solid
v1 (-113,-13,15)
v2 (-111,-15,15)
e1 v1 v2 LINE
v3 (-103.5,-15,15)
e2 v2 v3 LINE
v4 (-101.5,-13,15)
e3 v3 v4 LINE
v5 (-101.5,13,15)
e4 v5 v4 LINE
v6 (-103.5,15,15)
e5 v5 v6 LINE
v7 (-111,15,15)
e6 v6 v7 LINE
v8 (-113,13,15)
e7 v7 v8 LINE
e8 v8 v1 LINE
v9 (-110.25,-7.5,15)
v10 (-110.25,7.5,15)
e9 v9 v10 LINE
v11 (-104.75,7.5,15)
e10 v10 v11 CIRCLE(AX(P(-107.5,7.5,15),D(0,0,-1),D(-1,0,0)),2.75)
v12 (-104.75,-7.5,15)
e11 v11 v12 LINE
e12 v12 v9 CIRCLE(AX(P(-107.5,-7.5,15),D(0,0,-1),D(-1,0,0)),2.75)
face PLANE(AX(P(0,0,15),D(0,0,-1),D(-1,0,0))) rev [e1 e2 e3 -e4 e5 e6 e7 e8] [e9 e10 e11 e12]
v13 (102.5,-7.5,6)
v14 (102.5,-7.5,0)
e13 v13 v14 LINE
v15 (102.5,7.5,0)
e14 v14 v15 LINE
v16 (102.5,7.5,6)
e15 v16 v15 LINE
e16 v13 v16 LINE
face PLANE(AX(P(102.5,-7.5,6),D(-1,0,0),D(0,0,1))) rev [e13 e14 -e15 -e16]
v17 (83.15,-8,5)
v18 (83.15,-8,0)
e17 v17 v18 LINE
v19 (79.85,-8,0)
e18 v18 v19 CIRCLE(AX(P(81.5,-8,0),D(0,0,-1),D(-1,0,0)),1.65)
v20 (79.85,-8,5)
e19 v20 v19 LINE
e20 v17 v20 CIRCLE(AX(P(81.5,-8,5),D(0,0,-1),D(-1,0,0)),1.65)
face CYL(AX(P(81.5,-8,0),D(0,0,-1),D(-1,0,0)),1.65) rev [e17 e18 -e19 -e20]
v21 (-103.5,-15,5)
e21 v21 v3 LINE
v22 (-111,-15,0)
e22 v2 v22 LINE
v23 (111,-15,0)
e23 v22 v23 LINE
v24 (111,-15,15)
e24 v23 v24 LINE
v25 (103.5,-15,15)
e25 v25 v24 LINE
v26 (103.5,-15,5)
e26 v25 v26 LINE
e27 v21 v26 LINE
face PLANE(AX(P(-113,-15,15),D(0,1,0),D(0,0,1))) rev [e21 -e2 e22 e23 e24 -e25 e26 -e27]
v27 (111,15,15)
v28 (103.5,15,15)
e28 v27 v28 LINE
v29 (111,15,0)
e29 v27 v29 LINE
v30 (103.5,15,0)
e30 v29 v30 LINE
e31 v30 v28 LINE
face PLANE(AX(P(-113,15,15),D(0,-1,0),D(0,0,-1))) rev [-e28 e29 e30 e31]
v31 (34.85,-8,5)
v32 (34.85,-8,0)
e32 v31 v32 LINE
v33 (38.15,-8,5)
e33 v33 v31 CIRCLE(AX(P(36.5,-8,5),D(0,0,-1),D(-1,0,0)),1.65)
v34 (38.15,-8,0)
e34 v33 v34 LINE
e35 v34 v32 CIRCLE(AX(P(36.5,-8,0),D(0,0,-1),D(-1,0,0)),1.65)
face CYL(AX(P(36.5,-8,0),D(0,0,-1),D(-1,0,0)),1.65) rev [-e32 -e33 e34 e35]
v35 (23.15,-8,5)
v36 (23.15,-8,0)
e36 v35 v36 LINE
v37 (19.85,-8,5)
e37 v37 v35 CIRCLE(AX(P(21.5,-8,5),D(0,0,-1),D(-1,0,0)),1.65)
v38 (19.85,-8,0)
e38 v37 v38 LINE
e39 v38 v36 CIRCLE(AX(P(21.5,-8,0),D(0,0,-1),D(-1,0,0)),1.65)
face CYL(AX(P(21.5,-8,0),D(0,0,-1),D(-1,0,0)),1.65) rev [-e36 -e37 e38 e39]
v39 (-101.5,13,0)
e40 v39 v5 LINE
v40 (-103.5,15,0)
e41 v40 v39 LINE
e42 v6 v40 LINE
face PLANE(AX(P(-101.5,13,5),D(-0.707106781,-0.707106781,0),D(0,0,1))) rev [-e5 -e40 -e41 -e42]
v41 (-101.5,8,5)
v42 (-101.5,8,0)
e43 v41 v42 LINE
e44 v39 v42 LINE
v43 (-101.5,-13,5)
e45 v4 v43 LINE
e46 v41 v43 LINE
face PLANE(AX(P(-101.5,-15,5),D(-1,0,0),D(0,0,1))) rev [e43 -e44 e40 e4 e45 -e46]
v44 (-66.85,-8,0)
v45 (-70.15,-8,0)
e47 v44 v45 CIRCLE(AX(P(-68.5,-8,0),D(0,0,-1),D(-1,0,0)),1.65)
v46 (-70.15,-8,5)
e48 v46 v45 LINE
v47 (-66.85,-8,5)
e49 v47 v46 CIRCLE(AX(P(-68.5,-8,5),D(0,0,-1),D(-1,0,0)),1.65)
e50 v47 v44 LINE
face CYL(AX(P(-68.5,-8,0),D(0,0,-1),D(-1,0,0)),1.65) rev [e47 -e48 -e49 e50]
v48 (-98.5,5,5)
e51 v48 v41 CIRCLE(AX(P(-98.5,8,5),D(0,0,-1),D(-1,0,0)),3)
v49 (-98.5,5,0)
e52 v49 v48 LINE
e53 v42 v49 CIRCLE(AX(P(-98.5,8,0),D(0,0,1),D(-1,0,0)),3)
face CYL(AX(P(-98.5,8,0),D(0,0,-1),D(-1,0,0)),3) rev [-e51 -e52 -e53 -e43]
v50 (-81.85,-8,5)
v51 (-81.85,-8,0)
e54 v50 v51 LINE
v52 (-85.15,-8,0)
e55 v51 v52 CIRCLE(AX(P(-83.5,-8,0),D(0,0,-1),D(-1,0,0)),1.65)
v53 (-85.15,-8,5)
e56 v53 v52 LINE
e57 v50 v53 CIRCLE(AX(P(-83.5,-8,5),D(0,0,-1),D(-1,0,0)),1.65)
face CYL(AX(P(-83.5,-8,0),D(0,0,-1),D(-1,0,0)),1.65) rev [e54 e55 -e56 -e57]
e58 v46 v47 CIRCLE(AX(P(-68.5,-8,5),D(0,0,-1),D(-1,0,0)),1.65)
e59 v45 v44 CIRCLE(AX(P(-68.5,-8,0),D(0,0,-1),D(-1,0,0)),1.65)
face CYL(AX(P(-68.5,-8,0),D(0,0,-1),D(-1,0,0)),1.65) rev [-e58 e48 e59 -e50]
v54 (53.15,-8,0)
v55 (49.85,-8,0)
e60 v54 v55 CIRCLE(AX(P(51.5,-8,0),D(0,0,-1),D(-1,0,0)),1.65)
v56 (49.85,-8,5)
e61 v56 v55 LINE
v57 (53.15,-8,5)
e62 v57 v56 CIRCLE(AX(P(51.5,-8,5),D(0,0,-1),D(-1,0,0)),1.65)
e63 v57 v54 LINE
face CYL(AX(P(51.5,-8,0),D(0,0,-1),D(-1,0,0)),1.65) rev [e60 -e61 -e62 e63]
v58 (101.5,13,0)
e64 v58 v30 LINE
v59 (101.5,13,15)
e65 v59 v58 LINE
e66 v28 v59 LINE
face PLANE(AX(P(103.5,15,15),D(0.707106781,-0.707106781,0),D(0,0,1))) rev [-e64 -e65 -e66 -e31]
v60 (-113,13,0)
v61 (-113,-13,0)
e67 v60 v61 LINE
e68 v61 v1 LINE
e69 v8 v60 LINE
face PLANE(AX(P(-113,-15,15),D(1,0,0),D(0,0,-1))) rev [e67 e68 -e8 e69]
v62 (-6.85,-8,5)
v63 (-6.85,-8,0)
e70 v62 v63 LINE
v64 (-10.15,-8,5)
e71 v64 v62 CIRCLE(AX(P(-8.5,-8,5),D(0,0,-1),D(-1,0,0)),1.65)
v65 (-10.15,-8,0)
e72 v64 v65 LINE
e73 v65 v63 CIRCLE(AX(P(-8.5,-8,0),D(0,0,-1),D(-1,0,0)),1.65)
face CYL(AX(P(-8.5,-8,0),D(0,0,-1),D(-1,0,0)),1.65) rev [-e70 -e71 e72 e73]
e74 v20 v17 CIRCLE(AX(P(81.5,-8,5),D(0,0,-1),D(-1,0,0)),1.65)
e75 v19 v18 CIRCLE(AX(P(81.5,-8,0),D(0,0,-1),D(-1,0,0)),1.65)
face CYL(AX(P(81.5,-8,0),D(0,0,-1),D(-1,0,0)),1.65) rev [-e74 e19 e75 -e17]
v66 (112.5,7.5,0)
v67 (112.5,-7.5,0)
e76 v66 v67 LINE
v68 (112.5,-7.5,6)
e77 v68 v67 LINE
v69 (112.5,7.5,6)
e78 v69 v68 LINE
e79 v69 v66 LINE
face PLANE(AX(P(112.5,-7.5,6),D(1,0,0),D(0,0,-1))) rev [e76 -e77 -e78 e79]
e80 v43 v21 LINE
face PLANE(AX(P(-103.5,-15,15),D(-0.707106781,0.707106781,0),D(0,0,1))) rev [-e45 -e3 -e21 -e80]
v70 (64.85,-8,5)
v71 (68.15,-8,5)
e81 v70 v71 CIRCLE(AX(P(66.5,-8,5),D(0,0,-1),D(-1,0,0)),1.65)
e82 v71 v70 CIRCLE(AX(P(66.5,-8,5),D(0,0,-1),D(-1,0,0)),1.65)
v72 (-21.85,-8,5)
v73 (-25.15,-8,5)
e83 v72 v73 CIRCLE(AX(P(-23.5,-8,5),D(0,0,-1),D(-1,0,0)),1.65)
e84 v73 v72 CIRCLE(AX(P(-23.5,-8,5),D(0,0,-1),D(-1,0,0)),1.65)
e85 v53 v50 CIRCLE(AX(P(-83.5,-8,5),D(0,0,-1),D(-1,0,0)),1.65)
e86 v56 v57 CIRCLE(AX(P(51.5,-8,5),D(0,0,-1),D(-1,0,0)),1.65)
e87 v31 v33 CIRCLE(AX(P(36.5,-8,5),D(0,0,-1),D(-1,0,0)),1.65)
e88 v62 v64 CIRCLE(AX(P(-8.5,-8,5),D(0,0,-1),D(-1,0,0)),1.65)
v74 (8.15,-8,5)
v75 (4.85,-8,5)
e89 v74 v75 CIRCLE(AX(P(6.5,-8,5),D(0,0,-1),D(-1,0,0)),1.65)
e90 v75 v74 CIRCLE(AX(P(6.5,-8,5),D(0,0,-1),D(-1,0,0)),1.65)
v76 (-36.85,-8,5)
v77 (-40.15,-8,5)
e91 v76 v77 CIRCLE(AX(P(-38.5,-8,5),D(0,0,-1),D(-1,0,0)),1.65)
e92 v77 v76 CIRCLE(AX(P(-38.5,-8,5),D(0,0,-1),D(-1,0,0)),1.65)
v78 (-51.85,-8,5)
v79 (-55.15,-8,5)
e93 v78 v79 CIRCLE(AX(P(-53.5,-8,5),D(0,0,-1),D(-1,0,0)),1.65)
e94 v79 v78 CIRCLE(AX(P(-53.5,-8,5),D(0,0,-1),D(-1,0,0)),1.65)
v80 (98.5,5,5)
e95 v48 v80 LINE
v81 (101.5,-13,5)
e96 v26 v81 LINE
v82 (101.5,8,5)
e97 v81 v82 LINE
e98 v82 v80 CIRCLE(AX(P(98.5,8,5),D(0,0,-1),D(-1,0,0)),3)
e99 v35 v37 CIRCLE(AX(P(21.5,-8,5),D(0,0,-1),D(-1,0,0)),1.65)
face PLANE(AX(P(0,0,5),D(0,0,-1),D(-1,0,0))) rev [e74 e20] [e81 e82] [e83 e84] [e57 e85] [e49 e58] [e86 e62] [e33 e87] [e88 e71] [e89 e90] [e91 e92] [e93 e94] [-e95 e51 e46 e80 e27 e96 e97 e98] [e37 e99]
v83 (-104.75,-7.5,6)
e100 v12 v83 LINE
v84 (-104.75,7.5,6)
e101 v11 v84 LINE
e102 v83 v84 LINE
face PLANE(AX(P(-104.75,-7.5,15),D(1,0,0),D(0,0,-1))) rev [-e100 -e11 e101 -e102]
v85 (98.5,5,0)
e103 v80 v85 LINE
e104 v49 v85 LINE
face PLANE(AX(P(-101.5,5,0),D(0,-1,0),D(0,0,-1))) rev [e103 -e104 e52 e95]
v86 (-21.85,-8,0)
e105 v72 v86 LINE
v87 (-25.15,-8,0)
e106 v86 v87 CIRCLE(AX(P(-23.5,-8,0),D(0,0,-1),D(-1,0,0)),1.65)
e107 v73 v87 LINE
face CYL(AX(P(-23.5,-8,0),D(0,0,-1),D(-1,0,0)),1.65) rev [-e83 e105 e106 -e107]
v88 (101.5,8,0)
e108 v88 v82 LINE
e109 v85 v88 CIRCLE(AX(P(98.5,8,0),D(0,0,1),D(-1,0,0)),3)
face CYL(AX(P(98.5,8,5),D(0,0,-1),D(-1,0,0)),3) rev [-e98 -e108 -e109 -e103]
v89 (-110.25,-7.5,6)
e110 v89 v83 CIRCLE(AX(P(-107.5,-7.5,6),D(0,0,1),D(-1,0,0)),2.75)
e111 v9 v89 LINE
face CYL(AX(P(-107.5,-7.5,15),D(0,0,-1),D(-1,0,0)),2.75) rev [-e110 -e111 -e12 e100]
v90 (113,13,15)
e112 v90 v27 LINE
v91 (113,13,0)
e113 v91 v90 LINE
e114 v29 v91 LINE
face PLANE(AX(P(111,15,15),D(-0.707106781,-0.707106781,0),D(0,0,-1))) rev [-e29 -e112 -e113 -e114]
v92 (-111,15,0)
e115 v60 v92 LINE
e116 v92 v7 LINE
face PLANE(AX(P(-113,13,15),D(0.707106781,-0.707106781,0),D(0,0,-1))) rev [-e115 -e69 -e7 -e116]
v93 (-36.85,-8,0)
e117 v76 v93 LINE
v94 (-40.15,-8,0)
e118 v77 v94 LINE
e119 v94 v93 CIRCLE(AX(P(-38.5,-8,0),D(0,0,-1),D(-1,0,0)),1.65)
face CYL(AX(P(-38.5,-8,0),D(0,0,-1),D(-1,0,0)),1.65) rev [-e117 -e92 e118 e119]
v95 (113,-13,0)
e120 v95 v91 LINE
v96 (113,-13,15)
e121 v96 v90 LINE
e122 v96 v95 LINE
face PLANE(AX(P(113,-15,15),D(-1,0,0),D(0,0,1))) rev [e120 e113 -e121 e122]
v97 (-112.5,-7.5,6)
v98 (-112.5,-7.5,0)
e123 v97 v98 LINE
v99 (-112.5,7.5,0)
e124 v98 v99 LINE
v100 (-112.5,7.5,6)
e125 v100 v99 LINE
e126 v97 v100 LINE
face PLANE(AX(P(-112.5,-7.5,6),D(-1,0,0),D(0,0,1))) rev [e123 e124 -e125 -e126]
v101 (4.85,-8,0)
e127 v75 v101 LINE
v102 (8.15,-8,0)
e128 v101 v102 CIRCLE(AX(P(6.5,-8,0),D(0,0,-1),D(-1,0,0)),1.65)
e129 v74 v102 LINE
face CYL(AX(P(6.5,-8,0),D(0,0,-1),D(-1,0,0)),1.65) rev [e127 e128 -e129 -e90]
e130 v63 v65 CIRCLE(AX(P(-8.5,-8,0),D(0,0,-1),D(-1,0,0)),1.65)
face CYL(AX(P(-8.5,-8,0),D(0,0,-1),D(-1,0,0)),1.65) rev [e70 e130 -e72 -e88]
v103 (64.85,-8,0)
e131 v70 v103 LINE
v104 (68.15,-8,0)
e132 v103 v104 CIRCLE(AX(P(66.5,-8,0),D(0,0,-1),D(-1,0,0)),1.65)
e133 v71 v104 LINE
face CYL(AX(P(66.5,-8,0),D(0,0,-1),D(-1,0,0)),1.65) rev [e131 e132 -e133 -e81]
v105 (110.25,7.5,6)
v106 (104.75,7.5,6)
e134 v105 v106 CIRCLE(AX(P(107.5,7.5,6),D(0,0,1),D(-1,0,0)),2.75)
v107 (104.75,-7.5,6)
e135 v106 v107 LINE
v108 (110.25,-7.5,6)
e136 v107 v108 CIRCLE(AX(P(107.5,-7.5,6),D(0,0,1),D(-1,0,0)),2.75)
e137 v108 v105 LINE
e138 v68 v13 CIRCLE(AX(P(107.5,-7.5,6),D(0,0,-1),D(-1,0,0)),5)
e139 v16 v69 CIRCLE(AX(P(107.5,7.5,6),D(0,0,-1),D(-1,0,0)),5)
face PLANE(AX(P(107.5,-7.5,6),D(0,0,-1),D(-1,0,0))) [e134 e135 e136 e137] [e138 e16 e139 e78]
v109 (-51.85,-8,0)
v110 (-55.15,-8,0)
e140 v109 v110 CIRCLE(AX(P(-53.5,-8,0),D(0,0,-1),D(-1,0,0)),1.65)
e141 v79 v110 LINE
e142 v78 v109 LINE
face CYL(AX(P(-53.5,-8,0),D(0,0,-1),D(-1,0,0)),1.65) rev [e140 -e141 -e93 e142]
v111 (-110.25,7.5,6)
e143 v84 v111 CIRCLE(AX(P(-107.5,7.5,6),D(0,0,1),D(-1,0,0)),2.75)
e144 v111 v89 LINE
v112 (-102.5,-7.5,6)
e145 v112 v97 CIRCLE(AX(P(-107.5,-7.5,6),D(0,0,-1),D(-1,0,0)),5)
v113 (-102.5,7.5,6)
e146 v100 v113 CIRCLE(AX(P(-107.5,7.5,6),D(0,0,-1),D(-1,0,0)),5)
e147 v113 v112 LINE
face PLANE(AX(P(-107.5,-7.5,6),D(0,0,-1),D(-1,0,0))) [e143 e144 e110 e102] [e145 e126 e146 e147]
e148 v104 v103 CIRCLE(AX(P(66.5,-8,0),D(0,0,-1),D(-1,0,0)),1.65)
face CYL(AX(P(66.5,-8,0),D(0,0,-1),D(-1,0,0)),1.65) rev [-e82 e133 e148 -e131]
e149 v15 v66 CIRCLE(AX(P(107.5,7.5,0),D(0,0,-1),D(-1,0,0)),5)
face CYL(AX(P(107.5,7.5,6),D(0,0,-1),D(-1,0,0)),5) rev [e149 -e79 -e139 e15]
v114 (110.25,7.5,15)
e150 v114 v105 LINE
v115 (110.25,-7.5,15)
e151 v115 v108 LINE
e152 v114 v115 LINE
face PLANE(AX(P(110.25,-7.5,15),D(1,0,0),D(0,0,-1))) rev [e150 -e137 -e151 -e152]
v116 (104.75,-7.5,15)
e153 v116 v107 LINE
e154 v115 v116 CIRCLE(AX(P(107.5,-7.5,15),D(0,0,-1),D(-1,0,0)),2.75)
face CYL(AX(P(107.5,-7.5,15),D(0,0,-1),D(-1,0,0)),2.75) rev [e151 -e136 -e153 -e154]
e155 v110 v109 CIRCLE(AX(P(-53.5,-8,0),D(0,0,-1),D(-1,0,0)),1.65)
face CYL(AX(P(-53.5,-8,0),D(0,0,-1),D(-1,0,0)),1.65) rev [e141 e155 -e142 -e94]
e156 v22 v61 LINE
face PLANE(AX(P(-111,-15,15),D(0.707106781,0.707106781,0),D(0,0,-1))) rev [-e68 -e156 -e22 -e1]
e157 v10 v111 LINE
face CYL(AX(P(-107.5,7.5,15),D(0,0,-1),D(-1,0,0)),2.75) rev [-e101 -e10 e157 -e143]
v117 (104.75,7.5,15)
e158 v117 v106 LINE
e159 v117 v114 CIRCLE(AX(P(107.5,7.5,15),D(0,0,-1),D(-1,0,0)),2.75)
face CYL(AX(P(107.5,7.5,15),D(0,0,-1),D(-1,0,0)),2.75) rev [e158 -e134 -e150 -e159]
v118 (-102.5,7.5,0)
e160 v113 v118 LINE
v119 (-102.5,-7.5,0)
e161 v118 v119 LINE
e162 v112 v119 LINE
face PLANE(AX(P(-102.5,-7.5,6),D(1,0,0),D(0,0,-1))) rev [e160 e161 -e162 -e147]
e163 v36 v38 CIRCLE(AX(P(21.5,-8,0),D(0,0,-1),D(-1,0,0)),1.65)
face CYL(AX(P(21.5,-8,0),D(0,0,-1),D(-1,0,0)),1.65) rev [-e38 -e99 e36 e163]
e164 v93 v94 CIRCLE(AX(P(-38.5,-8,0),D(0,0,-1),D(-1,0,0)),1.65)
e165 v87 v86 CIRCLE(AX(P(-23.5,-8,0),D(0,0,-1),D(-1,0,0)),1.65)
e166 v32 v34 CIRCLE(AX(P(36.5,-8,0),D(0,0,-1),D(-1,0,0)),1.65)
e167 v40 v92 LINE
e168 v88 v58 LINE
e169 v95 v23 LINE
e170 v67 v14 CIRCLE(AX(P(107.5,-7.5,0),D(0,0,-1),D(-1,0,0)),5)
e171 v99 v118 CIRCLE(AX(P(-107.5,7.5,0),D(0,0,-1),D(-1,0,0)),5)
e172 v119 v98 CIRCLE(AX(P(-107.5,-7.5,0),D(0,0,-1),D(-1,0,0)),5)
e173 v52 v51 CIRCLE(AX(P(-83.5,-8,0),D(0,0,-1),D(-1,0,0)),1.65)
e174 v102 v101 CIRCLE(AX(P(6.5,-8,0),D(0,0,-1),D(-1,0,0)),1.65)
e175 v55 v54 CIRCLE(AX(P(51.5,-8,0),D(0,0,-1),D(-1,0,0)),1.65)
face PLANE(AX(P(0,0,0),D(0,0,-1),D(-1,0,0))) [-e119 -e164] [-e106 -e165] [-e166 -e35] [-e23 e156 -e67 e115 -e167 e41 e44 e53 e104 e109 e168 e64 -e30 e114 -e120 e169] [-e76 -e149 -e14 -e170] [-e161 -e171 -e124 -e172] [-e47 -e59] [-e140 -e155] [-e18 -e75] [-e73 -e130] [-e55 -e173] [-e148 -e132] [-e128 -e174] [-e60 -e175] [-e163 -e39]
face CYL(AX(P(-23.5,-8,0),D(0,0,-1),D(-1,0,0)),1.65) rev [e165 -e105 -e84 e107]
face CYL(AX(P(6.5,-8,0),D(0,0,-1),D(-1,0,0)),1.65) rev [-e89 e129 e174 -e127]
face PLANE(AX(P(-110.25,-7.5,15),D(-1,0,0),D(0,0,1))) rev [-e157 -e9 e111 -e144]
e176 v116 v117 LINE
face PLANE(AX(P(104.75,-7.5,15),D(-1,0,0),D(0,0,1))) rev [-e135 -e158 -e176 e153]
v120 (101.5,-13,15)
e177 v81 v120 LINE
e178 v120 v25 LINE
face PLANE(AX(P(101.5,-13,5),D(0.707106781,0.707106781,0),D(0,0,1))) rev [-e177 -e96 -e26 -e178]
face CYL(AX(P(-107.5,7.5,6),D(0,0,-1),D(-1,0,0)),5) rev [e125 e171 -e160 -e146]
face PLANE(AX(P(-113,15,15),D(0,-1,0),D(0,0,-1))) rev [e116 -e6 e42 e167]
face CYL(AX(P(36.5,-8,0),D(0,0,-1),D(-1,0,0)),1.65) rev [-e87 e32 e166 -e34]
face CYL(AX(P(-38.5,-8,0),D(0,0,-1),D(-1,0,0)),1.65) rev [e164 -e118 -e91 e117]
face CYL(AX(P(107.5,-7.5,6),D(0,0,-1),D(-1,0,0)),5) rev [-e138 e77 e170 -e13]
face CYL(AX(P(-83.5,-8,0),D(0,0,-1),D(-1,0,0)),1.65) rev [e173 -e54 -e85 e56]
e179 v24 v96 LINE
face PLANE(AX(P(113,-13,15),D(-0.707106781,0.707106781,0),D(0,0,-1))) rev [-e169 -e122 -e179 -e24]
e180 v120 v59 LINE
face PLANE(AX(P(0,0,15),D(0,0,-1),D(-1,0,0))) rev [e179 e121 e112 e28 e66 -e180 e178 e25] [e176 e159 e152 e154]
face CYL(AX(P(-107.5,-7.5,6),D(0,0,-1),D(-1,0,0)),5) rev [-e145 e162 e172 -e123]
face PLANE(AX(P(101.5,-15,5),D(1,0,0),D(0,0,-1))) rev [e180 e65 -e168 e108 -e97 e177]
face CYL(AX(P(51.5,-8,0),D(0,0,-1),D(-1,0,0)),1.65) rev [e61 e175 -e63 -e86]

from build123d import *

# Parameters (mm, degrees)
SKETCH_1_W             = 226
SKETCH_1_H             = 30
EXTRUDE_1_DEPTH        = 15
SKETCH_2_W             = 203
SKETCH_2_H             = 30
CUT_EXTRUDE_1_DEPTH    = 10
SKETCH_3_W             = 203
SKETCH_3_H             = 10
CUT_EXTRUDE_2_DEPTH    = 115.429017299
CUT_EXTRUDE_3_DEPTH    = 115.973910084
CUT_EXTRUDE_4_DEPTH    = 6
HOLE_WIZARD_M4_1_D     = 3.3
PATTERN_LINEAR_1_COUNT = 12
PATTERN_LINEAR_1_PITCH = 15
CHAMFER_1_SIZE         = 2
FILLET_1_R             = 3


with BuildPart() as part:
    # 草图1 → 凸台-拉伸1 (new body)
    with BuildSketch(Plane.XY):
        Rectangle(SKETCH_1_W, SKETCH_1_H)
    extrude(amount=EXTRUDE_1_DEPTH)

    # 草图2 → 切除-拉伸1 (cut)
    with BuildSketch(Plane.XY.offset(15)):
        Rectangle(SKETCH_2_W, SKETCH_2_H)
    extrude(amount=-CUT_EXTRUDE_1_DEPTH, mode=Mode.SUBTRACT)

    # 草图3 → 切除-拉伸2 (cut, through all)
    with BuildSketch(Plane.XY.offset(5)):
        with Locations((0, 10)):
            Rectangle(SKETCH_3_W, SKETCH_3_H)
    extrude(amount=-CUT_EXTRUDE_2_DEPTH, mode=Mode.SUBTRACT)

    # 草图4 → 切除-拉伸3 (cut, through all)
    with BuildSketch(Plane(origin=(0, 0, 0), x_dir=(-1, 0, 0), z_dir=(0, 0, -1))):
        with BuildLine():
            Line((104.75, -7.5), (104.75, 7.5))
            ThreePointArc((104.75, 7.5), (107.5, 10.25), (110.25, 7.5))
            Line((110.25, 7.5), (110.25, -7.5))
            ThreePointArc((110.25, -7.5), (107.5, -10.25), (104.75, -7.5))
        make_face()
        with BuildLine():
            Line((-110.25, -7.5), (-110.25, 7.5))
            ThreePointArc((-110.25, 7.5), (-107.5, 10.25), (-104.75, 7.5))
            Line((-104.75, 7.5), (-104.75, -7.5))
            ThreePointArc((-104.75, -7.5), (-107.5, -10.25), (-110.25, -7.5))
        make_face()
    extrude(amount=-CUT_EXTRUDE_3_DEPTH, mode=Mode.SUBTRACT)

    # 草图5 → 切除-拉伸4 (cut)
    with BuildSketch(Plane(origin=(0, 0, 0), x_dir=(-1, 0, 0), z_dir=(0, 0, -1))):
        with BuildLine():
            Line((102.5, -7.5), (102.5, 7.5))
            ThreePointArc((102.5, 7.5), (107.5, 12.5), (112.5, 7.5))
            Line((112.5, 7.5), (112.5, -7.5))
            ThreePointArc((112.5, -7.5), (107.5, -12.5), (102.5, -7.5))
        make_face()
        with BuildLine():
            Line((-112.5, -7.5), (-112.5, 7.5))
            ThreePointArc((-112.5, 7.5), (-107.5, 12.5), (-102.5, 7.5))
            Line((-102.5, 7.5), (-102.5, -7.5))
            ThreePointArc((-102.5, -7.5), (-107.5, -12.5), (-112.5, -7.5))
        make_face()
    extrude(amount=-CUT_EXTRUDE_4_DEPTH, mode=Mode.SUBTRACT)

    # M4 螺纹孔1 (through all)
    with Locations(Plane(origin=(0, 0, 0), x_dir=(-1, 0, 0), z_dir=(0, 0, -1))):
        with Locations((-81.5, -8)):
            hole_wizard_m4_1 = Hole(HOLE_WIZARD_M4_1_D / 2)

    # 阵列(线性)1: M4 螺纹孔1 ×12
    with Locations(*[(-i * PATTERN_LINEAR_1_PITCH, 0, 0) for i in range(1, PATTERN_LINEAR_1_COUNT)]):
        add(hole_wizard_m4_1, mode=Mode.SUBTRACT)

    # 倒角1
    chamfer_1_edges = [part.edges().sort_by_distance(p)[0] for p in [
        (101.5, 15, 7.5),
        (101.5, -15, 10),
        (-101.5, -15, 10),
        (-101.5, 15, 7.5),
        (113, -15, 7.5),
        (-113, -15, 7.5),
        (-113, 15, 7.5),
        (113, 15, 7.5),
    ]]
    chamfer(chamfer_1_edges, length=CHAMFER_1_SIZE)

    # 圆角1
    fillet_1_edges = [part.edges().sort_by_distance(p)[0] for p in [
        (-101.5, 5, 2.5),
        (101.5, 5, 2.5),
    ]]
    fillet(fillet_1_edges, radius=FILLET_1_R)


solid = part.part
